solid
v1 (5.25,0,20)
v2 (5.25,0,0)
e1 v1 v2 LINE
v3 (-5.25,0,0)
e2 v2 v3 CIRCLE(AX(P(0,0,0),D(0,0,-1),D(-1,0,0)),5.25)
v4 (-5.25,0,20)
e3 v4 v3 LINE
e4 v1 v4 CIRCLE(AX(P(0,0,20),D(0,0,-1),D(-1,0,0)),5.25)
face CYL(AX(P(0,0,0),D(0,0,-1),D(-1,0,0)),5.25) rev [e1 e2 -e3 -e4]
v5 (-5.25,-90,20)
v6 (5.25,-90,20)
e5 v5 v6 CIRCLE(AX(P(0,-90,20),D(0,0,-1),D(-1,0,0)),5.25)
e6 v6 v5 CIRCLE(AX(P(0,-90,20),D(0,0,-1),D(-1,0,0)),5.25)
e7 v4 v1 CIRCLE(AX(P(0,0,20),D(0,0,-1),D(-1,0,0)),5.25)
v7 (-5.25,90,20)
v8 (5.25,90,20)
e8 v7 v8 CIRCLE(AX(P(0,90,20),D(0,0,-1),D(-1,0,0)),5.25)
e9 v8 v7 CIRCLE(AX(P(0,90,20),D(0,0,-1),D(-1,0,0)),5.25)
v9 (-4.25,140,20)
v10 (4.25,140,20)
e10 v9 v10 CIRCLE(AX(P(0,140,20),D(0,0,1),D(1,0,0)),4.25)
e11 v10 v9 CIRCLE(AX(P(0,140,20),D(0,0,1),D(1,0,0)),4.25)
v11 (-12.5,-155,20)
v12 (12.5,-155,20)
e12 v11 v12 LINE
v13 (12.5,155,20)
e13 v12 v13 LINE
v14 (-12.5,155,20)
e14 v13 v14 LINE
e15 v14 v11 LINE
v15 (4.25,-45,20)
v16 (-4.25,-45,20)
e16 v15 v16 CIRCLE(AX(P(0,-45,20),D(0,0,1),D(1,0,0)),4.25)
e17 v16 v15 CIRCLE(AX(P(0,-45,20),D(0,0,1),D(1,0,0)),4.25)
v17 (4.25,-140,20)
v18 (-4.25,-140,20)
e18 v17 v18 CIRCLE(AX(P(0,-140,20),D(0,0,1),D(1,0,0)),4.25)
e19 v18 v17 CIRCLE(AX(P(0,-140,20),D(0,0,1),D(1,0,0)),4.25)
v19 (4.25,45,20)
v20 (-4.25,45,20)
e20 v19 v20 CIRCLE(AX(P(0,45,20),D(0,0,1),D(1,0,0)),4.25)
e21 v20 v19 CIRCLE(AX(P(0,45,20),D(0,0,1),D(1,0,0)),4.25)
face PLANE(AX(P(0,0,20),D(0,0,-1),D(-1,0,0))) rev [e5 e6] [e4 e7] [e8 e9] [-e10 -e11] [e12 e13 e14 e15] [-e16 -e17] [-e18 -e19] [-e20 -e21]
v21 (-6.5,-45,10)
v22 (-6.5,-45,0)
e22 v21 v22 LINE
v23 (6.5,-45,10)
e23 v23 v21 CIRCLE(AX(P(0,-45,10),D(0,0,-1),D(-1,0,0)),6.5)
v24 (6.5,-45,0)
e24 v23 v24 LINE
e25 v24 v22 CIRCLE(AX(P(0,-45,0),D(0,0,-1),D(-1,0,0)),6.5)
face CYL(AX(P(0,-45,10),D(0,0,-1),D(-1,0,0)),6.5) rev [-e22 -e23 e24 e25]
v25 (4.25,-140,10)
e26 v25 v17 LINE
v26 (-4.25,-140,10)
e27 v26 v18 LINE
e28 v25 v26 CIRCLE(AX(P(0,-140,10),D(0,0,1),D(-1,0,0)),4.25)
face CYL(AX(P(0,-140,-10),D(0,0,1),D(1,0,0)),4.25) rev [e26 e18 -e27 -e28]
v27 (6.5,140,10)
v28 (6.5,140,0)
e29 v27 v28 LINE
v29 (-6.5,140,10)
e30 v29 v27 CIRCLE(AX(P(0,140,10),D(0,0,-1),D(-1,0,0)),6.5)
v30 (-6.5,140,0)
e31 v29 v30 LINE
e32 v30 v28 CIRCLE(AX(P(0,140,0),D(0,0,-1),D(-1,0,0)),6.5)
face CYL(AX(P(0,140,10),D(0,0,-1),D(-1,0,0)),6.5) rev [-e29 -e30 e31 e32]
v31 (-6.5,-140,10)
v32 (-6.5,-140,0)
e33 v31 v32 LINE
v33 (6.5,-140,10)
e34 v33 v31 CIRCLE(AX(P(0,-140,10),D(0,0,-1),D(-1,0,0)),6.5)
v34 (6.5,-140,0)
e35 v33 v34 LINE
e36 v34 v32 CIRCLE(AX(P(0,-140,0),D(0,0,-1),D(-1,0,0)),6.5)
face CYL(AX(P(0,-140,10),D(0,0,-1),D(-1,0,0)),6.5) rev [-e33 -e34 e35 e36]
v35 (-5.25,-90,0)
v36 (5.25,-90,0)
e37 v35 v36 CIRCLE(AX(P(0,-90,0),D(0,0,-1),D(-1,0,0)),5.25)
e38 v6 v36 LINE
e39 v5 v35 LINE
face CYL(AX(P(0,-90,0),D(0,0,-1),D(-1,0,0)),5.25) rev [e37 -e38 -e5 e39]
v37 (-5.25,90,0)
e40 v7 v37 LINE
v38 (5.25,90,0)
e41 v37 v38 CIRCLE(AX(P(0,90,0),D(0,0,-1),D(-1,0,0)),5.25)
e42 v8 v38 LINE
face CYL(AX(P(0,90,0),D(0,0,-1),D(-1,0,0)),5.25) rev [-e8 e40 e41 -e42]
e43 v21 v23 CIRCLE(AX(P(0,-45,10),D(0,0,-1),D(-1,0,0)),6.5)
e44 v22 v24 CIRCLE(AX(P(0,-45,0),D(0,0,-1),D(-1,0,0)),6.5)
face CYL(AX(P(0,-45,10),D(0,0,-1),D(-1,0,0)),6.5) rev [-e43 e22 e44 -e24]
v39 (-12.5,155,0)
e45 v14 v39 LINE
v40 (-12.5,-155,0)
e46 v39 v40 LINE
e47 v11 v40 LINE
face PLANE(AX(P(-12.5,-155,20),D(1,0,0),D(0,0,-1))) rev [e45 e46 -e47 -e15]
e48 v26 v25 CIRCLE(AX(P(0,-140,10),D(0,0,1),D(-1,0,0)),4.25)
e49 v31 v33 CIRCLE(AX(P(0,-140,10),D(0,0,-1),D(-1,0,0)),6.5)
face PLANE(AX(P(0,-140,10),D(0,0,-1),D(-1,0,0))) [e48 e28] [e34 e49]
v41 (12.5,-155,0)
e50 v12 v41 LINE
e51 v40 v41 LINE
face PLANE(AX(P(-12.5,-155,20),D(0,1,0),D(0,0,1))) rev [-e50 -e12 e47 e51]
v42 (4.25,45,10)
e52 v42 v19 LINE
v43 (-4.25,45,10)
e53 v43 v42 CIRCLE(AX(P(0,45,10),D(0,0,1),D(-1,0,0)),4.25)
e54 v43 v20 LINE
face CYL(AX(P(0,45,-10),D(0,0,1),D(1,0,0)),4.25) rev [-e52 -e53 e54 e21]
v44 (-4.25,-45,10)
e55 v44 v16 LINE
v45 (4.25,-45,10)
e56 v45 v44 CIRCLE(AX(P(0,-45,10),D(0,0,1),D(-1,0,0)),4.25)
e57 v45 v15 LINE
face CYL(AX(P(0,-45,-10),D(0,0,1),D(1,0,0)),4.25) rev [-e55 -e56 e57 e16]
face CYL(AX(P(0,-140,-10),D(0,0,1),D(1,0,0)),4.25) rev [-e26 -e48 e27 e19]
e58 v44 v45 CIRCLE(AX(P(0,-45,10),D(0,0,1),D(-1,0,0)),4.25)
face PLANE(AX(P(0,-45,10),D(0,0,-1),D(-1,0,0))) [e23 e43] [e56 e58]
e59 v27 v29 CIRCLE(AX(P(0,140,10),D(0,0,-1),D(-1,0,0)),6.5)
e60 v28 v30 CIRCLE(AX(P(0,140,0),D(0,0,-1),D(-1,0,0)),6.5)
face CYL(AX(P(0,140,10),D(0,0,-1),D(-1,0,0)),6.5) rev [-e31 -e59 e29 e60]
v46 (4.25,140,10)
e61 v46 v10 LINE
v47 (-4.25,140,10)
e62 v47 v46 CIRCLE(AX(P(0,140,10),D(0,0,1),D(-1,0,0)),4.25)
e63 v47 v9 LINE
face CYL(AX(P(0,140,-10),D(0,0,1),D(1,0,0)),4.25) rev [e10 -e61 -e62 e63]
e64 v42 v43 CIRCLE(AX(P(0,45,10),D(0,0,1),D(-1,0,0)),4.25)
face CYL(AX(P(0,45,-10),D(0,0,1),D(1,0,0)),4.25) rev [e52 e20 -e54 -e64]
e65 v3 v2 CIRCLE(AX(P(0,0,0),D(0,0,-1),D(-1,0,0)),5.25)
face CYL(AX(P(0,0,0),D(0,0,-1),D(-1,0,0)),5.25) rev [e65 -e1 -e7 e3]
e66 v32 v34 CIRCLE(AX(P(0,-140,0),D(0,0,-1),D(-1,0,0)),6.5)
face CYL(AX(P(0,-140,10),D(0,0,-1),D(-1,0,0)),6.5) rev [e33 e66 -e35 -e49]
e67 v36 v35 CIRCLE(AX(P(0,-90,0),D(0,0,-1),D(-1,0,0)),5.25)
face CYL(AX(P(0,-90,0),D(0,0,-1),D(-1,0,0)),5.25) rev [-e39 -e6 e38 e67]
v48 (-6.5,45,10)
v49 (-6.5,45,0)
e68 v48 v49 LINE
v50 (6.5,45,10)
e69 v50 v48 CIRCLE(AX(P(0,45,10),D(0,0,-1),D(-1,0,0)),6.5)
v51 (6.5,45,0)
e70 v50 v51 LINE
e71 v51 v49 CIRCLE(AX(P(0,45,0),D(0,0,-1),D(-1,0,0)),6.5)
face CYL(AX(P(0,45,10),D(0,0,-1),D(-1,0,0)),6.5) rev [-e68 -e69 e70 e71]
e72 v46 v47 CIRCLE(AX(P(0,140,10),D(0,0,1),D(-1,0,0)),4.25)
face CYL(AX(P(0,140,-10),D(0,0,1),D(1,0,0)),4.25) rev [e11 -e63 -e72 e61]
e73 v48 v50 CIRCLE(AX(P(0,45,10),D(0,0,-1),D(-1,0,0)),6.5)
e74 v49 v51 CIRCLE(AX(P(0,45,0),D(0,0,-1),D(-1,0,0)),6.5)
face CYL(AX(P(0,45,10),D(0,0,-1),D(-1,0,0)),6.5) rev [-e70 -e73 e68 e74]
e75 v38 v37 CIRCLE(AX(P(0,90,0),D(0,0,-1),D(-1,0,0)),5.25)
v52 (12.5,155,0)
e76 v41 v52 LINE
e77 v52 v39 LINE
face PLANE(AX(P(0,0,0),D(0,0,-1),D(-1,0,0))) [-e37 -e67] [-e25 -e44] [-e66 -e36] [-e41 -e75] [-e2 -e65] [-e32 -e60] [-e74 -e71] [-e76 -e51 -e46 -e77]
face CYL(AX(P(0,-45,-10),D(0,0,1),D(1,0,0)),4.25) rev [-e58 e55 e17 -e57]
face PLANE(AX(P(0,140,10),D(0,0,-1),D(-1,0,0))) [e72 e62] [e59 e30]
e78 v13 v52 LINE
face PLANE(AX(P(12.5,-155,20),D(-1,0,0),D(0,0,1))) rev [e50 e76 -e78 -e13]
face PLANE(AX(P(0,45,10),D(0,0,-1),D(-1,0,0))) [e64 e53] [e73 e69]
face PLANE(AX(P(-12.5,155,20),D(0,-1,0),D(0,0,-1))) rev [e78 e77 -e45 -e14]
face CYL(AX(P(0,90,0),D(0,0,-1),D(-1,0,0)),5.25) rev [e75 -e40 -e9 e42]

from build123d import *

# Parameters (mm, degrees)
SKETCH1_W                   = 25
SKETCH1_H                   = 310
BOSS_EXTRUDE1_DEPTH         = 20
SKETCH3_R                   = 4.25
CUT_EXTRUDE1_DEPTH          = 30
SKETCH5_R                   = 6.5
CUT_EXTRUDE3_DEPTH          = 10
M12X1_25_TAPPED_HOLE1_D     = 10.5
M12X1_25_TAPPED_HOLE1_DEPTH = 30.25
M12X1_25_TAPPED_HOLE1_TIP   = 3.15451825


with BuildPart() as part:
    # Sketch1 → Boss-Extrude1 (new body)
    with BuildSketch(Plane.XY):
        Rectangle(SKETCH1_W, SKETCH1_H)
    extrude(amount=BOSS_EXTRUDE1_DEPTH)

    # Sketch3 → Cut-Extrude1 (cut)
    with BuildSketch(Plane.XY.offset(20)):
        with Locations((0, 140)):
            Circle(SKETCH3_R)
        with Locations((0, 45)):
            Circle(SKETCH3_R)
        with Locations((0, -45)):
            Circle(SKETCH3_R)
        with Locations((0, -140)):
            Circle(SKETCH3_R)
    extrude(amount=-CUT_EXTRUDE1_DEPTH, mode=Mode.SUBTRACT)

    # Sketch5 → Cut-Extrude3 (cut)
    with BuildSketch(Plane(origin=(0, 0, 0), x_dir=(-1, 0, 0), z_dir=(0, 0, -1))):
        with Locations((0, 140)):
            Circle(SKETCH5_R)
        with Locations((0, 45)):
            Circle(SKETCH5_R)
        with Locations((0, -45)):
            Circle(SKETCH5_R)
        with Locations((0, -140)):
            Circle(SKETCH5_R)
    extrude(amount=-CUT_EXTRUDE3_DEPTH, mode=Mode.SUBTRACT)

    # M12x1.25 Tapped Hole1
    with Locations(Plane(origin=(0, 0, 0), x_dir=(-1, 0, 0), z_dir=(0, 0, -1))):
        with Locations((0, 90), (0, 0), (0, -90)):
            Hole(M12X1_25_TAPPED_HOLE1_D / 2, depth=M12X1_25_TAPPED_HOLE1_DEPTH)
            with Locations((0, 0, -(M12X1_25_TAPPED_HOLE1_DEPTH + M12X1_25_TAPPED_HOLE1_TIP / 2))):  # 118° drill point
                Cone(0, M12X1_25_TAPPED_HOLE1_D / 2, M12X1_25_TAPPED_HOLE1_TIP, mode=Mode.SUBTRACT)


solid = part.part
